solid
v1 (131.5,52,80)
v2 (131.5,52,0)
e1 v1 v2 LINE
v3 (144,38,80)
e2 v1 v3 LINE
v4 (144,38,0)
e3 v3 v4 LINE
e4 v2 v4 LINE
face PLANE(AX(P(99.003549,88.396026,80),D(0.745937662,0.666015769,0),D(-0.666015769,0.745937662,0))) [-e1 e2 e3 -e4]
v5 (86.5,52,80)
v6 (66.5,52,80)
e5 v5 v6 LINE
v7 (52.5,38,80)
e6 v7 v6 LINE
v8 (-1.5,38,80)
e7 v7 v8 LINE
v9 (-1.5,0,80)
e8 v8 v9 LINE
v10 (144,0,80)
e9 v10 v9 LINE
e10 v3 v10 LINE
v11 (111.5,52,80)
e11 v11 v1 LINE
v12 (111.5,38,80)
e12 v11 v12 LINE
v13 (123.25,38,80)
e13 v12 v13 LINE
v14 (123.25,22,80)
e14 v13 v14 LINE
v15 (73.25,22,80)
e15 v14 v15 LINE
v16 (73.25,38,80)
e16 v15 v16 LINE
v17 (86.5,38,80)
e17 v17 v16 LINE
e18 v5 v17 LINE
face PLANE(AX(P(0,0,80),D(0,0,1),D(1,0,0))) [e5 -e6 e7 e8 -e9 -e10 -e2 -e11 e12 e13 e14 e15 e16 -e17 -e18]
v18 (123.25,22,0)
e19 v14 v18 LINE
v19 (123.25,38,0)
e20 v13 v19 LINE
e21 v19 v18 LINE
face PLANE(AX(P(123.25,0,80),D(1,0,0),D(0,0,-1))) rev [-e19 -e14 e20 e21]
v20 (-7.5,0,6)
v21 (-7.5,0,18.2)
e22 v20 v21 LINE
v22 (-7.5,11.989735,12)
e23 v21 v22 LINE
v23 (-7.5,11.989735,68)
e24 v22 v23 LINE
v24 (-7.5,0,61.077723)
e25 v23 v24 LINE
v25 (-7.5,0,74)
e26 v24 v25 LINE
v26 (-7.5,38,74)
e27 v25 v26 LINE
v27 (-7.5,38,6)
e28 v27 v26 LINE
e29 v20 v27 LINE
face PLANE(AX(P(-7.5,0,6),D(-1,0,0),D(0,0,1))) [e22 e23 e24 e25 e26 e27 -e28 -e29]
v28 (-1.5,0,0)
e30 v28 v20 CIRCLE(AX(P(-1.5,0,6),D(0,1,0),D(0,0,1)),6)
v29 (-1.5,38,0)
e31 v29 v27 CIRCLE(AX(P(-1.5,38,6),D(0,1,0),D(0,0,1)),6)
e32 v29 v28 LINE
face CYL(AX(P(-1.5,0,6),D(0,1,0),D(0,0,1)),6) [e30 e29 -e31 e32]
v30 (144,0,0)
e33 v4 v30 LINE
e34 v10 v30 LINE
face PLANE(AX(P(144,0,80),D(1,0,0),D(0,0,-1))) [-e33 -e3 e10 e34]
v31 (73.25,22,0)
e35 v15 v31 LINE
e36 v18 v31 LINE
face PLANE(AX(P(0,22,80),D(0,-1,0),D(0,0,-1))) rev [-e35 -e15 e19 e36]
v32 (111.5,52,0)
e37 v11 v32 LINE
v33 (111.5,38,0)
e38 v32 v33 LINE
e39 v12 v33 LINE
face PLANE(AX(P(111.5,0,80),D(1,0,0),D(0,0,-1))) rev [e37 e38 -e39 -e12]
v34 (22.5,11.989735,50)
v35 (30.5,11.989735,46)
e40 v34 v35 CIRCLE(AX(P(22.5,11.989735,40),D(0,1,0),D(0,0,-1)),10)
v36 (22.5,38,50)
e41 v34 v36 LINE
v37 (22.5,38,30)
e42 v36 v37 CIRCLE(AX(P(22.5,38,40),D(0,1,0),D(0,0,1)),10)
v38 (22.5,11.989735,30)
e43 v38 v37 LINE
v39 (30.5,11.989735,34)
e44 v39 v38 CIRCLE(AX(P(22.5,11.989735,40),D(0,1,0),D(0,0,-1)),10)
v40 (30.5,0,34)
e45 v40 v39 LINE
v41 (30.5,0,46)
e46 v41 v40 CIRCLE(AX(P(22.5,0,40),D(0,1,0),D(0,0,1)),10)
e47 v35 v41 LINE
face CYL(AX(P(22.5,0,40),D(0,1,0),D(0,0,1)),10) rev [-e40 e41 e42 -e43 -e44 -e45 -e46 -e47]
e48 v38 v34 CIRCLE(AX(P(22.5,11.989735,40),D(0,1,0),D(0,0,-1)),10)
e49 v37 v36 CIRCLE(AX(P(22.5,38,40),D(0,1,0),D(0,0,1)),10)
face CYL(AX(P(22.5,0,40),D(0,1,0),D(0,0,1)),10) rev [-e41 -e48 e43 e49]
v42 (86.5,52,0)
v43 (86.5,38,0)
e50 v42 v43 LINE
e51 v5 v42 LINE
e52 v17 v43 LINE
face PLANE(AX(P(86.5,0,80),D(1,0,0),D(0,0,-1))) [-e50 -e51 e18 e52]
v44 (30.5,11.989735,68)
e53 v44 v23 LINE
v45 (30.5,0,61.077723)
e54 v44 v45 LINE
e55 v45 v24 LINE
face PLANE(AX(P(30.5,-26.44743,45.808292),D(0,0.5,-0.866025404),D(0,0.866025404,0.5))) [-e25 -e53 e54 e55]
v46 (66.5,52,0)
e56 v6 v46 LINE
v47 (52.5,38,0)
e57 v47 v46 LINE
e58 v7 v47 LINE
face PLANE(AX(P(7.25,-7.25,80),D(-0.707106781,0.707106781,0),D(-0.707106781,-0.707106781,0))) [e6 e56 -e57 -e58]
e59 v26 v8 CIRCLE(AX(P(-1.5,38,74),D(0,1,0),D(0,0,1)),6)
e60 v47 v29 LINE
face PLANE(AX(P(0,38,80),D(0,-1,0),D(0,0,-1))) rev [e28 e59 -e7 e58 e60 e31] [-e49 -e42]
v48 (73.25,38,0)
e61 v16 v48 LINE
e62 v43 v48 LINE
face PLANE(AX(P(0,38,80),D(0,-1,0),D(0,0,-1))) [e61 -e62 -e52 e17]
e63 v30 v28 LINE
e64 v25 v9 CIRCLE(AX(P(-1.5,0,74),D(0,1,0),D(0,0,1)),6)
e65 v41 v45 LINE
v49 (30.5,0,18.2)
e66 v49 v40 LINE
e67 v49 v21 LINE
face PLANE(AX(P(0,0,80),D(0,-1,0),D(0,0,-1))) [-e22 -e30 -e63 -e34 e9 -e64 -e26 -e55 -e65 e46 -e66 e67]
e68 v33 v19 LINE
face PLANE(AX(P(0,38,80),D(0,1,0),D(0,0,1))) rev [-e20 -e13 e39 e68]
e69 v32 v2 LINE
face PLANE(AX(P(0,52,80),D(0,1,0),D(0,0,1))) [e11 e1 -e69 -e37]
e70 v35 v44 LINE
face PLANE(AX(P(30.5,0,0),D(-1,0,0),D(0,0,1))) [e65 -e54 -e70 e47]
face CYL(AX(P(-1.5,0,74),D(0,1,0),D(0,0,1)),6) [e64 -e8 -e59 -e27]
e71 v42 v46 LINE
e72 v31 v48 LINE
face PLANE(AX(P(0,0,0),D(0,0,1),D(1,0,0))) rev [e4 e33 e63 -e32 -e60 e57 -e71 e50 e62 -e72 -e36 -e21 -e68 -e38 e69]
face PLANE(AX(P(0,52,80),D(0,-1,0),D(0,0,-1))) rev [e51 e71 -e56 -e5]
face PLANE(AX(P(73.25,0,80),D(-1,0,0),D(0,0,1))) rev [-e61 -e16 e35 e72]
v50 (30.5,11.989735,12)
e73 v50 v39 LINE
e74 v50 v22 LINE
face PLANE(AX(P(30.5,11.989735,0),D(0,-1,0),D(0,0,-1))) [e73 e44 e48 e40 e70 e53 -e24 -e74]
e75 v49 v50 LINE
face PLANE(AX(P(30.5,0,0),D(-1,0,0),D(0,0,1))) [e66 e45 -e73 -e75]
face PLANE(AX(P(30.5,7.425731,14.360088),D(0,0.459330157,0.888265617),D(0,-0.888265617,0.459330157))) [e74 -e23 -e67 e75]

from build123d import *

# Parameters (mm, degrees)
BASE_BODY_DEPTH    = 80
RAISED_BLOCK_DEPTH = 38
WEDGE_BOSS_DEPTH   = 80
TOP_HOLE_SKETCH_R  = 10
TOP_HOLE_DEPTH     = 38
PROFILE_CUT_DEPTH  = 38


with BuildPart() as part:
    # Base Profile Sketch → Base Body (new body)
    with BuildSketch(Plane.XY):
        with BuildLine():
            Line((52.5, 0), (54, 0))
            Line((54, 0), (144, 0))
            Line((144, 0), (144, 22))
            Line((144, 22), (144, 38))
            Line((144, 38), (131.5, 52))
            Line((131.5, 52), (111.5, 52))
            Line((111.5, 52), (111.5, 38))
            Line((111.5, 38), (123.25, 38))
            Line((123.25, 38), (123.25, 22))
            Line((123.25, 22), (73.25, 22))
            Line((73.25, 22), (73.25, 38))
            Line((73.25, 38), (86.5, 38))
            Line((86.5, 38), (86.5, 52))
            Line((86.5, 52), (66.5, 52))
            Line((66.5, 52), (52.5, 38))
            Line((52.5, 38), (-1.5, 38))
            Line((-1.5, 38), (-1.5, 0))
            ThreePointArc((-1.5, 0), (-0.743974245, 0.047821822), (0, 0.190524981))
            Line((0, 0.190524981), (0, 0))
            Line((0, 0), (52.5, 0))
        make_face()
    extrude(amount=BASE_BODY_DEPTH)

    # Raised Block Sketch → Raised Block (add)
    with BuildSketch(Plane(origin=(0, 38, 0), x_dir=(1, 0, 0), z_dir=(0, 1, 0))):
        with BuildLine():
            Line((-1.5, 0), (-1.5, -6))
            Line((-1.5, -6), (-1.5, -74))
            Line((-1.5, -74), (-1.5, -80))
            ThreePointArc((-1.5, -80), (-5.742640687, -78.242640687), (-7.5, -74))
            Line((-7.5, -74), (-7.5, -6))
            ThreePointArc((-7.5, -6), (-5.742640687, -1.757359313), (-1.5, 0))
        make_face()
    extrude(amount=-RAISED_BLOCK_DEPTH)

    # Wedge Sketch → Wedge Boss (add)
    with BuildSketch(Plane(origin=(0, 0, 0), x_dir=(-1, 0, 0), z_dir=(0, 0, -1))):
        Polygon((0, 0.190524981), (0, 0), (1.5, 0), align=None)
    extrude(amount=-WEDGE_BOSS_DEPTH)

    # Top Hole Sketch → Top Hole (cut)
    with BuildSketch(Plane(origin=(0, 38, 0), x_dir=(1, 0, 0), z_dir=(0, 1, 0))):
        with Locations(Location((22.5, -40, 0), (0, 0, 270))):
            Circle(TOP_HOLE_SKETCH_R)
    extrude(amount=-TOP_HOLE_DEPTH, mode=Mode.SUBTRACT)

    # Profile Cut Sketch → Profile Cut (cut)
    with BuildSketch(Plane.ZY.offset(7.5)):
        Polygon((68, 11.989734921), (40, 11.989734921), (12, 11.989734921), (18.2, 0), (40, 0), (61.077723316, 0), align=None)
    extrude(amount=-PROFILE_CUT_DEPTH, mode=Mode.SUBTRACT)


solid = part.part
